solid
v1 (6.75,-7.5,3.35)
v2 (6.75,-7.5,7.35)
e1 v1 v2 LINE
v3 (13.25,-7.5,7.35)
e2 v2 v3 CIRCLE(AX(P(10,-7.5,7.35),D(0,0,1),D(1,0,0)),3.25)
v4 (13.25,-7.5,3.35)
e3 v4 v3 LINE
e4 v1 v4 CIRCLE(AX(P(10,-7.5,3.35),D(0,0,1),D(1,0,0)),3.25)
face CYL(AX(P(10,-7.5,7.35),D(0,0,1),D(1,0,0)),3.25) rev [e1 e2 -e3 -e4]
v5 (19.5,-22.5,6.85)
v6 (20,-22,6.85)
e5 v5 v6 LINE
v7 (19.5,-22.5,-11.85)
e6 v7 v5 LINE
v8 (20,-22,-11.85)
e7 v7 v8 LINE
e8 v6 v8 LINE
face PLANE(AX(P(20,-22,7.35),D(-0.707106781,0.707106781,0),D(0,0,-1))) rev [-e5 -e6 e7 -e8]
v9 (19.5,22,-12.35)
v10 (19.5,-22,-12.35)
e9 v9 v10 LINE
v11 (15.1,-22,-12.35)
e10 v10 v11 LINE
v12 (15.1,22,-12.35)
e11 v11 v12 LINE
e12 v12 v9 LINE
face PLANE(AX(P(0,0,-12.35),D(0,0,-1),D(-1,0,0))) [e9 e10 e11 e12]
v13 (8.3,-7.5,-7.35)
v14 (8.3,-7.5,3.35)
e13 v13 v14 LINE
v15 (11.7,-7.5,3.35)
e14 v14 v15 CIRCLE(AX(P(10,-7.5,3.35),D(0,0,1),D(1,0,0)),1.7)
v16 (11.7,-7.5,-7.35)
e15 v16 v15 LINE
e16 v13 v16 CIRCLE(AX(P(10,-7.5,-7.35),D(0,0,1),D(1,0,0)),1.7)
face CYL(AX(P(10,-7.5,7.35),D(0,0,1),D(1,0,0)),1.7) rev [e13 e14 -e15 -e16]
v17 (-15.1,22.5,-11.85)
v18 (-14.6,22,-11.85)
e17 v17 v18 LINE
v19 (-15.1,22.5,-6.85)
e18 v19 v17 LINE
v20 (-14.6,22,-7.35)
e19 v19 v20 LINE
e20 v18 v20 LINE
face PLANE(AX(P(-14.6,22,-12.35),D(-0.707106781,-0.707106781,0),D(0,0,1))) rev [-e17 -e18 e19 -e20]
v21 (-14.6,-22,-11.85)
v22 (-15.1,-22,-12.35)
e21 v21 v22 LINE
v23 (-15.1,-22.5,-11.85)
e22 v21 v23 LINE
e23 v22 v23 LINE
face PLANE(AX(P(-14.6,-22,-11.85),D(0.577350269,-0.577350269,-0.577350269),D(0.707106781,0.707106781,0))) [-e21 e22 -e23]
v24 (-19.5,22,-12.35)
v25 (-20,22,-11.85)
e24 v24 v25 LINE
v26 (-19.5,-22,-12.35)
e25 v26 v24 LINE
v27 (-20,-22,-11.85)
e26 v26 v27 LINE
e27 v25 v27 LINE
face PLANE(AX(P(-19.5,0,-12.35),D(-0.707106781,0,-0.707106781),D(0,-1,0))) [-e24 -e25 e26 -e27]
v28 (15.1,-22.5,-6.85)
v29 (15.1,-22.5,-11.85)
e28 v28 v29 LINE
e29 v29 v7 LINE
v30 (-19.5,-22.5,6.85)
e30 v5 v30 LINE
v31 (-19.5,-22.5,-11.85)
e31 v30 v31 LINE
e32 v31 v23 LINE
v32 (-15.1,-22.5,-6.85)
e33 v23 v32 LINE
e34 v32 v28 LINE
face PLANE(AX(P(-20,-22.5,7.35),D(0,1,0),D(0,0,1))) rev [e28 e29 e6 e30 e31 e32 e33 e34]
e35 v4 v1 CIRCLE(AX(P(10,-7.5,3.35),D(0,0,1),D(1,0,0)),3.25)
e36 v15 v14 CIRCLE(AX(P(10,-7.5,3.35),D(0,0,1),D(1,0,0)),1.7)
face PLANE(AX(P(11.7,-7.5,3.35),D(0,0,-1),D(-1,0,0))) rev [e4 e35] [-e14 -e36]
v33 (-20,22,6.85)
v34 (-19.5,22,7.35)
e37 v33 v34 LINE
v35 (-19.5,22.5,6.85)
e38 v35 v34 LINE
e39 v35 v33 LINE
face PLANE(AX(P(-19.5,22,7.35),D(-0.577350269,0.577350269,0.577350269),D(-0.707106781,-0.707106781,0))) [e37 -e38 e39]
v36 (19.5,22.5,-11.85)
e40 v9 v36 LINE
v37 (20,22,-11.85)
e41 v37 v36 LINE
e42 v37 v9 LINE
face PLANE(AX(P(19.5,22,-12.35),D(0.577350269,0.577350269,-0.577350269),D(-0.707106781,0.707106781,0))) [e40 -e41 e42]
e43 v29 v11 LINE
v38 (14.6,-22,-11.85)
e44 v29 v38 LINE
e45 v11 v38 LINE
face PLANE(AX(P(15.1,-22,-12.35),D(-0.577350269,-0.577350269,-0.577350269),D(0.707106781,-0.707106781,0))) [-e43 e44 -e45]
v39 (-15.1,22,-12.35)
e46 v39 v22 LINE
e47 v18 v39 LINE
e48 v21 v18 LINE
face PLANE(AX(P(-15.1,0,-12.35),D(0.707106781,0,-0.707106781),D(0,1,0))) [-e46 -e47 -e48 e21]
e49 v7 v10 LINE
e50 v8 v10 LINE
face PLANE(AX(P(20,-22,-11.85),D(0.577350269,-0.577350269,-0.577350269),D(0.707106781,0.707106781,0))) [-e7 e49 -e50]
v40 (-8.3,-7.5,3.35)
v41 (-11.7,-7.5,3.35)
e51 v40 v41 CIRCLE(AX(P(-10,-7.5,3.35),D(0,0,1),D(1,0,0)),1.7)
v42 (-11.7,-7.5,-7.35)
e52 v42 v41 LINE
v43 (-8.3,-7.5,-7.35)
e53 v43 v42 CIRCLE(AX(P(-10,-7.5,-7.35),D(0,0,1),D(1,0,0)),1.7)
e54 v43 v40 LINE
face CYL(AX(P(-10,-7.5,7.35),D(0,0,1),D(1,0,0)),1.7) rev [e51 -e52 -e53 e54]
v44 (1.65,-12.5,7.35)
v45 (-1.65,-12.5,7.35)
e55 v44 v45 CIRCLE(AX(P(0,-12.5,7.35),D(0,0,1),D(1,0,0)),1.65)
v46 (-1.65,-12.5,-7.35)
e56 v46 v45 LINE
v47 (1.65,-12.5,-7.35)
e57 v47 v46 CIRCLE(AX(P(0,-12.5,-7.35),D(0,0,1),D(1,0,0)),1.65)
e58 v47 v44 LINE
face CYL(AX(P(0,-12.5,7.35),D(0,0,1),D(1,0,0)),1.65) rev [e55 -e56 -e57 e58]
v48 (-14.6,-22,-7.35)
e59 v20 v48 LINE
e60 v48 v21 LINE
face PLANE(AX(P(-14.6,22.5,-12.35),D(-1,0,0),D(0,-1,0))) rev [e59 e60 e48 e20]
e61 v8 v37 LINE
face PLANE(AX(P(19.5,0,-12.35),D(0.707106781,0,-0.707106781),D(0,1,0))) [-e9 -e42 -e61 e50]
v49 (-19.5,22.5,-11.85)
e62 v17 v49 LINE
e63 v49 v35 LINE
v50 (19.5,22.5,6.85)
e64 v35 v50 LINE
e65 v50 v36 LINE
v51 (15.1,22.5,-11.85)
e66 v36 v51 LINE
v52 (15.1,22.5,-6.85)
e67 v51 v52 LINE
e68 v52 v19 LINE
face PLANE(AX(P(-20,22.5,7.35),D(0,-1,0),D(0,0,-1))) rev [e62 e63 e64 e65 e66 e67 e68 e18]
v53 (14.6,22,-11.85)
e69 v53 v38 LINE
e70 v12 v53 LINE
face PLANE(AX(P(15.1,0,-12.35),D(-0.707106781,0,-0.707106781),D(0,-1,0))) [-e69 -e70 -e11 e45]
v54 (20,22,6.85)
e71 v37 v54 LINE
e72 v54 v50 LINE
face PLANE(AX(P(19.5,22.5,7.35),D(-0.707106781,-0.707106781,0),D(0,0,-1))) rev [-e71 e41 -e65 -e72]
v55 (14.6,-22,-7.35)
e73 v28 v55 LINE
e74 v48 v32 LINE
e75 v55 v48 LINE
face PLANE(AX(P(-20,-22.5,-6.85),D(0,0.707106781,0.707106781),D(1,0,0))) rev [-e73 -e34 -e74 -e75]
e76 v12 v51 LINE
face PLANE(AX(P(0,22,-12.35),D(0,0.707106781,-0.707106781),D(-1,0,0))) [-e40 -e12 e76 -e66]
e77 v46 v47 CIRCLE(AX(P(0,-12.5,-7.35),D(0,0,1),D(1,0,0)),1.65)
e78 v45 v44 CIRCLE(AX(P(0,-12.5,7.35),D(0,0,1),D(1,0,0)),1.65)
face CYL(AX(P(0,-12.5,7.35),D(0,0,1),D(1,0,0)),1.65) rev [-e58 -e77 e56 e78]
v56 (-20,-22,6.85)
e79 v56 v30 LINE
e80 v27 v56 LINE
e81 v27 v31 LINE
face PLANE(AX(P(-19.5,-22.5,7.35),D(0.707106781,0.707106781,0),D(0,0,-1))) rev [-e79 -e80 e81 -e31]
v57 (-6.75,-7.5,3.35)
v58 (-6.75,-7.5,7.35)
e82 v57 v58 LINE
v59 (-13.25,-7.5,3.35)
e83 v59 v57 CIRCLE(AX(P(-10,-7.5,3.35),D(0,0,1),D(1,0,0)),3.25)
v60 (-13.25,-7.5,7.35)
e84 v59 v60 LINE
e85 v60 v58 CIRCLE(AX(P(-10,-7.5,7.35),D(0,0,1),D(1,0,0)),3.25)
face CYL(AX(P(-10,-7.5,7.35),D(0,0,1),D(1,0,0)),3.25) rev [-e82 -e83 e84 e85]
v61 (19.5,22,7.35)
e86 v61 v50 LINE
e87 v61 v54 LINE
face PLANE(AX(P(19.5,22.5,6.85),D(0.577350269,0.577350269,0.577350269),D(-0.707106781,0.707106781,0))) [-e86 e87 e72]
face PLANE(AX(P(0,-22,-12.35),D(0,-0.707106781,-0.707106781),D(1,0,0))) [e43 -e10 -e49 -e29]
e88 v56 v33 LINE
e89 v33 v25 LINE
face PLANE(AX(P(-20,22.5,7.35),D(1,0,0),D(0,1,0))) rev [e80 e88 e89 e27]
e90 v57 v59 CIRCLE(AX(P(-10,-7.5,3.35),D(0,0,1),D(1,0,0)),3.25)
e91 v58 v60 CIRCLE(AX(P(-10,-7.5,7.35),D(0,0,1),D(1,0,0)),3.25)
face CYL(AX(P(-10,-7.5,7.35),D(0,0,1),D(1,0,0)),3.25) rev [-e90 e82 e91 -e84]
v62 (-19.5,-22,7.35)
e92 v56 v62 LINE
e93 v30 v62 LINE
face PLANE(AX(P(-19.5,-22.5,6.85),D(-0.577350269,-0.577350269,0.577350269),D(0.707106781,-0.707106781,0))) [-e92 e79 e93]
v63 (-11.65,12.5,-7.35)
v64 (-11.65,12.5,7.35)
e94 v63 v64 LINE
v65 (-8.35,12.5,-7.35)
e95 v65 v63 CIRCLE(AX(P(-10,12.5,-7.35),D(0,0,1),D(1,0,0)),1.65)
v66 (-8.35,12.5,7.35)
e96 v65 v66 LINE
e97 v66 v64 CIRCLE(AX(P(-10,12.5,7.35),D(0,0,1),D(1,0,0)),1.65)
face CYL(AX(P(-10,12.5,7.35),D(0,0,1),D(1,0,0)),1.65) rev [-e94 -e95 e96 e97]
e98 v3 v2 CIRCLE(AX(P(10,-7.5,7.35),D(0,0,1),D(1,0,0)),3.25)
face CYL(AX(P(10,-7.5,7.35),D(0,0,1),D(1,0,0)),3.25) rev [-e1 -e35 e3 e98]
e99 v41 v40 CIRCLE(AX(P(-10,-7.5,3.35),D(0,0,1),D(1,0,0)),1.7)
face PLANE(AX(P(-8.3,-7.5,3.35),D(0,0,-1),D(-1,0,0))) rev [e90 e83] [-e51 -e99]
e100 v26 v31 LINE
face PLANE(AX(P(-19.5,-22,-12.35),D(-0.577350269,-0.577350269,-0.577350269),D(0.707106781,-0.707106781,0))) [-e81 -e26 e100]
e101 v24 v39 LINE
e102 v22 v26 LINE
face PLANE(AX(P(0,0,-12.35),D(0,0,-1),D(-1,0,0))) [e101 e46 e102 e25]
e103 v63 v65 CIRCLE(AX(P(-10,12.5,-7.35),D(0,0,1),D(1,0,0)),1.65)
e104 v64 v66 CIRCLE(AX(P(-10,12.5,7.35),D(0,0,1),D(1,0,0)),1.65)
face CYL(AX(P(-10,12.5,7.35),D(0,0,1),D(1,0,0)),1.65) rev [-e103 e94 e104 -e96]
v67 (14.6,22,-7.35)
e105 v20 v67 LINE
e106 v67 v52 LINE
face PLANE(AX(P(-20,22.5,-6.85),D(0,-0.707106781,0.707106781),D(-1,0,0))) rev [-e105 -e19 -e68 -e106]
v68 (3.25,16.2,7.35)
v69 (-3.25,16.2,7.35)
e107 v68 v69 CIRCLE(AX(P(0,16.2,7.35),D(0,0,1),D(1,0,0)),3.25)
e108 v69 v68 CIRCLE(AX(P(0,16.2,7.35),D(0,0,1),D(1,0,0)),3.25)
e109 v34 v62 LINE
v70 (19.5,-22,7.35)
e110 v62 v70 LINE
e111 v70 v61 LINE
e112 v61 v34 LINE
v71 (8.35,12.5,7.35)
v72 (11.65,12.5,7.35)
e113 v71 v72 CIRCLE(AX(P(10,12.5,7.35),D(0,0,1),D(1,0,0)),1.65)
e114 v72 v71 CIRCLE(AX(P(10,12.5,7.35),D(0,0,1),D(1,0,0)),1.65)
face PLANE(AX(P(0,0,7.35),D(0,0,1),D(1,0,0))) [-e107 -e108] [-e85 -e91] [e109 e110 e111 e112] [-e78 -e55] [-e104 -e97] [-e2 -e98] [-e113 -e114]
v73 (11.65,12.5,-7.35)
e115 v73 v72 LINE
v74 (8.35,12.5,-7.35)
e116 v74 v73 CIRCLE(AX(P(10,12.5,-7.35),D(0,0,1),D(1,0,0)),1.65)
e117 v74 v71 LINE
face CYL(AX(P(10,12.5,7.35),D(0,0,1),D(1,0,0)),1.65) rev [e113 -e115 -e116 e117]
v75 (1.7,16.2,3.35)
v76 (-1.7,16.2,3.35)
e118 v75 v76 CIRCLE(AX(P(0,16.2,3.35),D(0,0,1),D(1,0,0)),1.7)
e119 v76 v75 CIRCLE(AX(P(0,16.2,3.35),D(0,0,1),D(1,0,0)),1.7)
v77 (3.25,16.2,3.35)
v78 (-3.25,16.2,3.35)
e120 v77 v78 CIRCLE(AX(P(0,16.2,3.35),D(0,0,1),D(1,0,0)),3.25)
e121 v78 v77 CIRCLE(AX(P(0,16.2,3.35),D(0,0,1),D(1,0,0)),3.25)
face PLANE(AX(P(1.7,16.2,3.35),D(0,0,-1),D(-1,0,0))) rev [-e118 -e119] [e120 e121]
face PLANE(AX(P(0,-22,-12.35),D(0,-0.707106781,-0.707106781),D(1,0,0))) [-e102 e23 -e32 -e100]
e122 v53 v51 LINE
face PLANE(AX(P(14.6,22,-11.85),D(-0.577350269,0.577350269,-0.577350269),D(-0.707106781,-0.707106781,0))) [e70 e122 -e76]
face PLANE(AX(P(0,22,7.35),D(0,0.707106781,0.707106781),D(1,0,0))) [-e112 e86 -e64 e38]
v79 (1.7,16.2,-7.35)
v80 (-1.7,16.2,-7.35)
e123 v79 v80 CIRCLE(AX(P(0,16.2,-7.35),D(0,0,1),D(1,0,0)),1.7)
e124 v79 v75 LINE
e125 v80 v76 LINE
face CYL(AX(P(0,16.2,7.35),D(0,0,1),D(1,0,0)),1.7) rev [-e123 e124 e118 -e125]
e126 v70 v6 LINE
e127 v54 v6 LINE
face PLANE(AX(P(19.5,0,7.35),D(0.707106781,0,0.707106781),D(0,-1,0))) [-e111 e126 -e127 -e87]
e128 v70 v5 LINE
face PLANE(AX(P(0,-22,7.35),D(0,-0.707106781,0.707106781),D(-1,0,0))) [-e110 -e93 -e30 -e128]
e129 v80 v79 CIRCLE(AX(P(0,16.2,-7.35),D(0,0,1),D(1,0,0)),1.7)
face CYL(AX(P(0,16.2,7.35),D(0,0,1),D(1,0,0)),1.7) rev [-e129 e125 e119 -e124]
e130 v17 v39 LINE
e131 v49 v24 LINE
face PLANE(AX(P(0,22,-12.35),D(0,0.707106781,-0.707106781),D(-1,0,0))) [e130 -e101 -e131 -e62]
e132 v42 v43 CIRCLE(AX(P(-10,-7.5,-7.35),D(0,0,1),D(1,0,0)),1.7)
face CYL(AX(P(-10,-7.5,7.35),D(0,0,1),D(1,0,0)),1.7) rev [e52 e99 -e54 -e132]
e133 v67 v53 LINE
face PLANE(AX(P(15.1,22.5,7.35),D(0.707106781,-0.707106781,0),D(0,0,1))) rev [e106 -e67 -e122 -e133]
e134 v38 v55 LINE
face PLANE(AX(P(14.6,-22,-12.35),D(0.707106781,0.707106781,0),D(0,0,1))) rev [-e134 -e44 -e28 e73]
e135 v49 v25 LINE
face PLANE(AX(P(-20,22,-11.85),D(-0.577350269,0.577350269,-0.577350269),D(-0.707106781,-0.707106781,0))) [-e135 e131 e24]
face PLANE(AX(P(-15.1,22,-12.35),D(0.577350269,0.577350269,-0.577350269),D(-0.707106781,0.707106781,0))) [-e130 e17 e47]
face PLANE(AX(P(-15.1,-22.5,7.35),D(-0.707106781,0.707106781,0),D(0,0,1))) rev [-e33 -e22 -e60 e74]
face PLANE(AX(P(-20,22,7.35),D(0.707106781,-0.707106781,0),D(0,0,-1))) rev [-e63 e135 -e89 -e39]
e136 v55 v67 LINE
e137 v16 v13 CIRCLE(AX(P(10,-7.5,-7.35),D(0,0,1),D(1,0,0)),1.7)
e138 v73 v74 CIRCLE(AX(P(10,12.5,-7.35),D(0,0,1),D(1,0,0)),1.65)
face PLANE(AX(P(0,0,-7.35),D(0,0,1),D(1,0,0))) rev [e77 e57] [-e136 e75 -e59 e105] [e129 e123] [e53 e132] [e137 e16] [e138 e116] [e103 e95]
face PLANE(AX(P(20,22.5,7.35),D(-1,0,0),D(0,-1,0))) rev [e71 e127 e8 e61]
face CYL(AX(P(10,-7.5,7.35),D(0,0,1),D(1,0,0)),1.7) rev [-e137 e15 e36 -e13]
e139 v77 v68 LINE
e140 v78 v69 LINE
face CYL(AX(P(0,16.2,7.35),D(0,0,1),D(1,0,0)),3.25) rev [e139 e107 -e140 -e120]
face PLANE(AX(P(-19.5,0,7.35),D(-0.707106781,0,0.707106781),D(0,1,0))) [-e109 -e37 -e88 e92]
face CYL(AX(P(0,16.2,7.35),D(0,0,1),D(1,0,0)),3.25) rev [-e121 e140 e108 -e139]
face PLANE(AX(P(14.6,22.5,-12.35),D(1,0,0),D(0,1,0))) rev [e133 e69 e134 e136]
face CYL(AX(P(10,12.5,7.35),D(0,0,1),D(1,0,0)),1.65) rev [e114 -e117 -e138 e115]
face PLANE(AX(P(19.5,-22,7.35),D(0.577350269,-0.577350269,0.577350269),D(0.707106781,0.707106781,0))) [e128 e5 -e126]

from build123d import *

# Parameters (mm, degrees)
SKETCH_1_W                   = 40
SKETCH_1_H                   = 45
EXTRUDE_1_DEPTH              = 7.35
HOLE_WIZARD_M3_1_D           = 3.4
HOLE_WIZARD_M3_1_CBORE_D     = 6.5
HOLE_WIZARD_M3_1_CBORE_DEPTH = 4
SKETCH_5_W                   = 5.4
SKETCH_5_H                   = 45
EXTRUDE_2_DEPTH              = 5
HOLE_WIZARD_M4_2_D           = 3.3
CHAMFER_1_SIZE               = 0.5


with BuildPart() as part:
    # 草图1 → 凸台-拉伸1 (new, symmetric)
    with BuildSketch(Plane.XY):
        Rectangle(SKETCH_1_W, SKETCH_1_H)
    extrude(amount=EXTRUDE_1_DEPTH, both=True)

    # M3 六角凹头螺钉的柱形沉头孔1 (through all)
    with Locations(Plane.XY.offset(7.35)):
        with Locations((0, 16.2), (-10, -7.5), (10, -7.5)):
            CounterBoreHole(HOLE_WIZARD_M3_1_D / 2, HOLE_WIZARD_M3_1_CBORE_D / 2, HOLE_WIZARD_M3_1_CBORE_DEPTH)

    # 草图5 → 凸台-拉伸2 (add)
    with BuildSketch(Plane(origin=(0, 0, -7.35), x_dir=(-1, 0, 0), z_dir=(0, 0, -1))):
        with Locations((-17.3, 0)):
            Rectangle(SKETCH_5_W, SKETCH_5_H)
        with Locations((17.3, 0)):
            Rectangle(SKETCH_5_W, SKETCH_5_H)
    extrude(amount=EXTRUDE_2_DEPTH)

    # M4 螺纹孔2 (through all)
    with Locations(Plane.XY.offset(7.35)):
        with Locations((10, 12.5), (-10, 12.5), (0, -12.5)):
            Hole(HOLE_WIZARD_M4_2_D / 2)

    # 倒角1
    chamfer_1_edges = [part.edges().sort_by_distance(p)[0] for p in [
        (-20, 0, 7.35),
        (0, -22.5, 7.35),
        (0, 22.5, -7.35),
        (14.6, -22.5, -9.85),
        (14.6, 22.5, -9.85),
        (20, 0, -12.35),
        (17.3, -22.5, -12.35),
        (14.6, 0, -12.35),
        (17.3, 22.5, -12.35),
        (20, 0, 7.35),
        (0, -22.5, -7.35),
        (-14.6, 22.5, -9.85),
        (-14.6, -22.5, -9.85),
        (-14.6, 0, -12.35),
        (-17.3, -22.5, -12.35),
        (-20, 0, -12.35),
        (-17.3, 22.5, -12.35),
        (0, 22.5, 7.35),
        (20, -22.5, -2.5),
        (-20, -22.5, -2.5),
        (-20, 22.5, -2.5),
        (20, 22.5, -2.5),
    ]]
    chamfer(chamfer_1_edges, length=CHAMFER_1_SIZE)


solid = part.part
